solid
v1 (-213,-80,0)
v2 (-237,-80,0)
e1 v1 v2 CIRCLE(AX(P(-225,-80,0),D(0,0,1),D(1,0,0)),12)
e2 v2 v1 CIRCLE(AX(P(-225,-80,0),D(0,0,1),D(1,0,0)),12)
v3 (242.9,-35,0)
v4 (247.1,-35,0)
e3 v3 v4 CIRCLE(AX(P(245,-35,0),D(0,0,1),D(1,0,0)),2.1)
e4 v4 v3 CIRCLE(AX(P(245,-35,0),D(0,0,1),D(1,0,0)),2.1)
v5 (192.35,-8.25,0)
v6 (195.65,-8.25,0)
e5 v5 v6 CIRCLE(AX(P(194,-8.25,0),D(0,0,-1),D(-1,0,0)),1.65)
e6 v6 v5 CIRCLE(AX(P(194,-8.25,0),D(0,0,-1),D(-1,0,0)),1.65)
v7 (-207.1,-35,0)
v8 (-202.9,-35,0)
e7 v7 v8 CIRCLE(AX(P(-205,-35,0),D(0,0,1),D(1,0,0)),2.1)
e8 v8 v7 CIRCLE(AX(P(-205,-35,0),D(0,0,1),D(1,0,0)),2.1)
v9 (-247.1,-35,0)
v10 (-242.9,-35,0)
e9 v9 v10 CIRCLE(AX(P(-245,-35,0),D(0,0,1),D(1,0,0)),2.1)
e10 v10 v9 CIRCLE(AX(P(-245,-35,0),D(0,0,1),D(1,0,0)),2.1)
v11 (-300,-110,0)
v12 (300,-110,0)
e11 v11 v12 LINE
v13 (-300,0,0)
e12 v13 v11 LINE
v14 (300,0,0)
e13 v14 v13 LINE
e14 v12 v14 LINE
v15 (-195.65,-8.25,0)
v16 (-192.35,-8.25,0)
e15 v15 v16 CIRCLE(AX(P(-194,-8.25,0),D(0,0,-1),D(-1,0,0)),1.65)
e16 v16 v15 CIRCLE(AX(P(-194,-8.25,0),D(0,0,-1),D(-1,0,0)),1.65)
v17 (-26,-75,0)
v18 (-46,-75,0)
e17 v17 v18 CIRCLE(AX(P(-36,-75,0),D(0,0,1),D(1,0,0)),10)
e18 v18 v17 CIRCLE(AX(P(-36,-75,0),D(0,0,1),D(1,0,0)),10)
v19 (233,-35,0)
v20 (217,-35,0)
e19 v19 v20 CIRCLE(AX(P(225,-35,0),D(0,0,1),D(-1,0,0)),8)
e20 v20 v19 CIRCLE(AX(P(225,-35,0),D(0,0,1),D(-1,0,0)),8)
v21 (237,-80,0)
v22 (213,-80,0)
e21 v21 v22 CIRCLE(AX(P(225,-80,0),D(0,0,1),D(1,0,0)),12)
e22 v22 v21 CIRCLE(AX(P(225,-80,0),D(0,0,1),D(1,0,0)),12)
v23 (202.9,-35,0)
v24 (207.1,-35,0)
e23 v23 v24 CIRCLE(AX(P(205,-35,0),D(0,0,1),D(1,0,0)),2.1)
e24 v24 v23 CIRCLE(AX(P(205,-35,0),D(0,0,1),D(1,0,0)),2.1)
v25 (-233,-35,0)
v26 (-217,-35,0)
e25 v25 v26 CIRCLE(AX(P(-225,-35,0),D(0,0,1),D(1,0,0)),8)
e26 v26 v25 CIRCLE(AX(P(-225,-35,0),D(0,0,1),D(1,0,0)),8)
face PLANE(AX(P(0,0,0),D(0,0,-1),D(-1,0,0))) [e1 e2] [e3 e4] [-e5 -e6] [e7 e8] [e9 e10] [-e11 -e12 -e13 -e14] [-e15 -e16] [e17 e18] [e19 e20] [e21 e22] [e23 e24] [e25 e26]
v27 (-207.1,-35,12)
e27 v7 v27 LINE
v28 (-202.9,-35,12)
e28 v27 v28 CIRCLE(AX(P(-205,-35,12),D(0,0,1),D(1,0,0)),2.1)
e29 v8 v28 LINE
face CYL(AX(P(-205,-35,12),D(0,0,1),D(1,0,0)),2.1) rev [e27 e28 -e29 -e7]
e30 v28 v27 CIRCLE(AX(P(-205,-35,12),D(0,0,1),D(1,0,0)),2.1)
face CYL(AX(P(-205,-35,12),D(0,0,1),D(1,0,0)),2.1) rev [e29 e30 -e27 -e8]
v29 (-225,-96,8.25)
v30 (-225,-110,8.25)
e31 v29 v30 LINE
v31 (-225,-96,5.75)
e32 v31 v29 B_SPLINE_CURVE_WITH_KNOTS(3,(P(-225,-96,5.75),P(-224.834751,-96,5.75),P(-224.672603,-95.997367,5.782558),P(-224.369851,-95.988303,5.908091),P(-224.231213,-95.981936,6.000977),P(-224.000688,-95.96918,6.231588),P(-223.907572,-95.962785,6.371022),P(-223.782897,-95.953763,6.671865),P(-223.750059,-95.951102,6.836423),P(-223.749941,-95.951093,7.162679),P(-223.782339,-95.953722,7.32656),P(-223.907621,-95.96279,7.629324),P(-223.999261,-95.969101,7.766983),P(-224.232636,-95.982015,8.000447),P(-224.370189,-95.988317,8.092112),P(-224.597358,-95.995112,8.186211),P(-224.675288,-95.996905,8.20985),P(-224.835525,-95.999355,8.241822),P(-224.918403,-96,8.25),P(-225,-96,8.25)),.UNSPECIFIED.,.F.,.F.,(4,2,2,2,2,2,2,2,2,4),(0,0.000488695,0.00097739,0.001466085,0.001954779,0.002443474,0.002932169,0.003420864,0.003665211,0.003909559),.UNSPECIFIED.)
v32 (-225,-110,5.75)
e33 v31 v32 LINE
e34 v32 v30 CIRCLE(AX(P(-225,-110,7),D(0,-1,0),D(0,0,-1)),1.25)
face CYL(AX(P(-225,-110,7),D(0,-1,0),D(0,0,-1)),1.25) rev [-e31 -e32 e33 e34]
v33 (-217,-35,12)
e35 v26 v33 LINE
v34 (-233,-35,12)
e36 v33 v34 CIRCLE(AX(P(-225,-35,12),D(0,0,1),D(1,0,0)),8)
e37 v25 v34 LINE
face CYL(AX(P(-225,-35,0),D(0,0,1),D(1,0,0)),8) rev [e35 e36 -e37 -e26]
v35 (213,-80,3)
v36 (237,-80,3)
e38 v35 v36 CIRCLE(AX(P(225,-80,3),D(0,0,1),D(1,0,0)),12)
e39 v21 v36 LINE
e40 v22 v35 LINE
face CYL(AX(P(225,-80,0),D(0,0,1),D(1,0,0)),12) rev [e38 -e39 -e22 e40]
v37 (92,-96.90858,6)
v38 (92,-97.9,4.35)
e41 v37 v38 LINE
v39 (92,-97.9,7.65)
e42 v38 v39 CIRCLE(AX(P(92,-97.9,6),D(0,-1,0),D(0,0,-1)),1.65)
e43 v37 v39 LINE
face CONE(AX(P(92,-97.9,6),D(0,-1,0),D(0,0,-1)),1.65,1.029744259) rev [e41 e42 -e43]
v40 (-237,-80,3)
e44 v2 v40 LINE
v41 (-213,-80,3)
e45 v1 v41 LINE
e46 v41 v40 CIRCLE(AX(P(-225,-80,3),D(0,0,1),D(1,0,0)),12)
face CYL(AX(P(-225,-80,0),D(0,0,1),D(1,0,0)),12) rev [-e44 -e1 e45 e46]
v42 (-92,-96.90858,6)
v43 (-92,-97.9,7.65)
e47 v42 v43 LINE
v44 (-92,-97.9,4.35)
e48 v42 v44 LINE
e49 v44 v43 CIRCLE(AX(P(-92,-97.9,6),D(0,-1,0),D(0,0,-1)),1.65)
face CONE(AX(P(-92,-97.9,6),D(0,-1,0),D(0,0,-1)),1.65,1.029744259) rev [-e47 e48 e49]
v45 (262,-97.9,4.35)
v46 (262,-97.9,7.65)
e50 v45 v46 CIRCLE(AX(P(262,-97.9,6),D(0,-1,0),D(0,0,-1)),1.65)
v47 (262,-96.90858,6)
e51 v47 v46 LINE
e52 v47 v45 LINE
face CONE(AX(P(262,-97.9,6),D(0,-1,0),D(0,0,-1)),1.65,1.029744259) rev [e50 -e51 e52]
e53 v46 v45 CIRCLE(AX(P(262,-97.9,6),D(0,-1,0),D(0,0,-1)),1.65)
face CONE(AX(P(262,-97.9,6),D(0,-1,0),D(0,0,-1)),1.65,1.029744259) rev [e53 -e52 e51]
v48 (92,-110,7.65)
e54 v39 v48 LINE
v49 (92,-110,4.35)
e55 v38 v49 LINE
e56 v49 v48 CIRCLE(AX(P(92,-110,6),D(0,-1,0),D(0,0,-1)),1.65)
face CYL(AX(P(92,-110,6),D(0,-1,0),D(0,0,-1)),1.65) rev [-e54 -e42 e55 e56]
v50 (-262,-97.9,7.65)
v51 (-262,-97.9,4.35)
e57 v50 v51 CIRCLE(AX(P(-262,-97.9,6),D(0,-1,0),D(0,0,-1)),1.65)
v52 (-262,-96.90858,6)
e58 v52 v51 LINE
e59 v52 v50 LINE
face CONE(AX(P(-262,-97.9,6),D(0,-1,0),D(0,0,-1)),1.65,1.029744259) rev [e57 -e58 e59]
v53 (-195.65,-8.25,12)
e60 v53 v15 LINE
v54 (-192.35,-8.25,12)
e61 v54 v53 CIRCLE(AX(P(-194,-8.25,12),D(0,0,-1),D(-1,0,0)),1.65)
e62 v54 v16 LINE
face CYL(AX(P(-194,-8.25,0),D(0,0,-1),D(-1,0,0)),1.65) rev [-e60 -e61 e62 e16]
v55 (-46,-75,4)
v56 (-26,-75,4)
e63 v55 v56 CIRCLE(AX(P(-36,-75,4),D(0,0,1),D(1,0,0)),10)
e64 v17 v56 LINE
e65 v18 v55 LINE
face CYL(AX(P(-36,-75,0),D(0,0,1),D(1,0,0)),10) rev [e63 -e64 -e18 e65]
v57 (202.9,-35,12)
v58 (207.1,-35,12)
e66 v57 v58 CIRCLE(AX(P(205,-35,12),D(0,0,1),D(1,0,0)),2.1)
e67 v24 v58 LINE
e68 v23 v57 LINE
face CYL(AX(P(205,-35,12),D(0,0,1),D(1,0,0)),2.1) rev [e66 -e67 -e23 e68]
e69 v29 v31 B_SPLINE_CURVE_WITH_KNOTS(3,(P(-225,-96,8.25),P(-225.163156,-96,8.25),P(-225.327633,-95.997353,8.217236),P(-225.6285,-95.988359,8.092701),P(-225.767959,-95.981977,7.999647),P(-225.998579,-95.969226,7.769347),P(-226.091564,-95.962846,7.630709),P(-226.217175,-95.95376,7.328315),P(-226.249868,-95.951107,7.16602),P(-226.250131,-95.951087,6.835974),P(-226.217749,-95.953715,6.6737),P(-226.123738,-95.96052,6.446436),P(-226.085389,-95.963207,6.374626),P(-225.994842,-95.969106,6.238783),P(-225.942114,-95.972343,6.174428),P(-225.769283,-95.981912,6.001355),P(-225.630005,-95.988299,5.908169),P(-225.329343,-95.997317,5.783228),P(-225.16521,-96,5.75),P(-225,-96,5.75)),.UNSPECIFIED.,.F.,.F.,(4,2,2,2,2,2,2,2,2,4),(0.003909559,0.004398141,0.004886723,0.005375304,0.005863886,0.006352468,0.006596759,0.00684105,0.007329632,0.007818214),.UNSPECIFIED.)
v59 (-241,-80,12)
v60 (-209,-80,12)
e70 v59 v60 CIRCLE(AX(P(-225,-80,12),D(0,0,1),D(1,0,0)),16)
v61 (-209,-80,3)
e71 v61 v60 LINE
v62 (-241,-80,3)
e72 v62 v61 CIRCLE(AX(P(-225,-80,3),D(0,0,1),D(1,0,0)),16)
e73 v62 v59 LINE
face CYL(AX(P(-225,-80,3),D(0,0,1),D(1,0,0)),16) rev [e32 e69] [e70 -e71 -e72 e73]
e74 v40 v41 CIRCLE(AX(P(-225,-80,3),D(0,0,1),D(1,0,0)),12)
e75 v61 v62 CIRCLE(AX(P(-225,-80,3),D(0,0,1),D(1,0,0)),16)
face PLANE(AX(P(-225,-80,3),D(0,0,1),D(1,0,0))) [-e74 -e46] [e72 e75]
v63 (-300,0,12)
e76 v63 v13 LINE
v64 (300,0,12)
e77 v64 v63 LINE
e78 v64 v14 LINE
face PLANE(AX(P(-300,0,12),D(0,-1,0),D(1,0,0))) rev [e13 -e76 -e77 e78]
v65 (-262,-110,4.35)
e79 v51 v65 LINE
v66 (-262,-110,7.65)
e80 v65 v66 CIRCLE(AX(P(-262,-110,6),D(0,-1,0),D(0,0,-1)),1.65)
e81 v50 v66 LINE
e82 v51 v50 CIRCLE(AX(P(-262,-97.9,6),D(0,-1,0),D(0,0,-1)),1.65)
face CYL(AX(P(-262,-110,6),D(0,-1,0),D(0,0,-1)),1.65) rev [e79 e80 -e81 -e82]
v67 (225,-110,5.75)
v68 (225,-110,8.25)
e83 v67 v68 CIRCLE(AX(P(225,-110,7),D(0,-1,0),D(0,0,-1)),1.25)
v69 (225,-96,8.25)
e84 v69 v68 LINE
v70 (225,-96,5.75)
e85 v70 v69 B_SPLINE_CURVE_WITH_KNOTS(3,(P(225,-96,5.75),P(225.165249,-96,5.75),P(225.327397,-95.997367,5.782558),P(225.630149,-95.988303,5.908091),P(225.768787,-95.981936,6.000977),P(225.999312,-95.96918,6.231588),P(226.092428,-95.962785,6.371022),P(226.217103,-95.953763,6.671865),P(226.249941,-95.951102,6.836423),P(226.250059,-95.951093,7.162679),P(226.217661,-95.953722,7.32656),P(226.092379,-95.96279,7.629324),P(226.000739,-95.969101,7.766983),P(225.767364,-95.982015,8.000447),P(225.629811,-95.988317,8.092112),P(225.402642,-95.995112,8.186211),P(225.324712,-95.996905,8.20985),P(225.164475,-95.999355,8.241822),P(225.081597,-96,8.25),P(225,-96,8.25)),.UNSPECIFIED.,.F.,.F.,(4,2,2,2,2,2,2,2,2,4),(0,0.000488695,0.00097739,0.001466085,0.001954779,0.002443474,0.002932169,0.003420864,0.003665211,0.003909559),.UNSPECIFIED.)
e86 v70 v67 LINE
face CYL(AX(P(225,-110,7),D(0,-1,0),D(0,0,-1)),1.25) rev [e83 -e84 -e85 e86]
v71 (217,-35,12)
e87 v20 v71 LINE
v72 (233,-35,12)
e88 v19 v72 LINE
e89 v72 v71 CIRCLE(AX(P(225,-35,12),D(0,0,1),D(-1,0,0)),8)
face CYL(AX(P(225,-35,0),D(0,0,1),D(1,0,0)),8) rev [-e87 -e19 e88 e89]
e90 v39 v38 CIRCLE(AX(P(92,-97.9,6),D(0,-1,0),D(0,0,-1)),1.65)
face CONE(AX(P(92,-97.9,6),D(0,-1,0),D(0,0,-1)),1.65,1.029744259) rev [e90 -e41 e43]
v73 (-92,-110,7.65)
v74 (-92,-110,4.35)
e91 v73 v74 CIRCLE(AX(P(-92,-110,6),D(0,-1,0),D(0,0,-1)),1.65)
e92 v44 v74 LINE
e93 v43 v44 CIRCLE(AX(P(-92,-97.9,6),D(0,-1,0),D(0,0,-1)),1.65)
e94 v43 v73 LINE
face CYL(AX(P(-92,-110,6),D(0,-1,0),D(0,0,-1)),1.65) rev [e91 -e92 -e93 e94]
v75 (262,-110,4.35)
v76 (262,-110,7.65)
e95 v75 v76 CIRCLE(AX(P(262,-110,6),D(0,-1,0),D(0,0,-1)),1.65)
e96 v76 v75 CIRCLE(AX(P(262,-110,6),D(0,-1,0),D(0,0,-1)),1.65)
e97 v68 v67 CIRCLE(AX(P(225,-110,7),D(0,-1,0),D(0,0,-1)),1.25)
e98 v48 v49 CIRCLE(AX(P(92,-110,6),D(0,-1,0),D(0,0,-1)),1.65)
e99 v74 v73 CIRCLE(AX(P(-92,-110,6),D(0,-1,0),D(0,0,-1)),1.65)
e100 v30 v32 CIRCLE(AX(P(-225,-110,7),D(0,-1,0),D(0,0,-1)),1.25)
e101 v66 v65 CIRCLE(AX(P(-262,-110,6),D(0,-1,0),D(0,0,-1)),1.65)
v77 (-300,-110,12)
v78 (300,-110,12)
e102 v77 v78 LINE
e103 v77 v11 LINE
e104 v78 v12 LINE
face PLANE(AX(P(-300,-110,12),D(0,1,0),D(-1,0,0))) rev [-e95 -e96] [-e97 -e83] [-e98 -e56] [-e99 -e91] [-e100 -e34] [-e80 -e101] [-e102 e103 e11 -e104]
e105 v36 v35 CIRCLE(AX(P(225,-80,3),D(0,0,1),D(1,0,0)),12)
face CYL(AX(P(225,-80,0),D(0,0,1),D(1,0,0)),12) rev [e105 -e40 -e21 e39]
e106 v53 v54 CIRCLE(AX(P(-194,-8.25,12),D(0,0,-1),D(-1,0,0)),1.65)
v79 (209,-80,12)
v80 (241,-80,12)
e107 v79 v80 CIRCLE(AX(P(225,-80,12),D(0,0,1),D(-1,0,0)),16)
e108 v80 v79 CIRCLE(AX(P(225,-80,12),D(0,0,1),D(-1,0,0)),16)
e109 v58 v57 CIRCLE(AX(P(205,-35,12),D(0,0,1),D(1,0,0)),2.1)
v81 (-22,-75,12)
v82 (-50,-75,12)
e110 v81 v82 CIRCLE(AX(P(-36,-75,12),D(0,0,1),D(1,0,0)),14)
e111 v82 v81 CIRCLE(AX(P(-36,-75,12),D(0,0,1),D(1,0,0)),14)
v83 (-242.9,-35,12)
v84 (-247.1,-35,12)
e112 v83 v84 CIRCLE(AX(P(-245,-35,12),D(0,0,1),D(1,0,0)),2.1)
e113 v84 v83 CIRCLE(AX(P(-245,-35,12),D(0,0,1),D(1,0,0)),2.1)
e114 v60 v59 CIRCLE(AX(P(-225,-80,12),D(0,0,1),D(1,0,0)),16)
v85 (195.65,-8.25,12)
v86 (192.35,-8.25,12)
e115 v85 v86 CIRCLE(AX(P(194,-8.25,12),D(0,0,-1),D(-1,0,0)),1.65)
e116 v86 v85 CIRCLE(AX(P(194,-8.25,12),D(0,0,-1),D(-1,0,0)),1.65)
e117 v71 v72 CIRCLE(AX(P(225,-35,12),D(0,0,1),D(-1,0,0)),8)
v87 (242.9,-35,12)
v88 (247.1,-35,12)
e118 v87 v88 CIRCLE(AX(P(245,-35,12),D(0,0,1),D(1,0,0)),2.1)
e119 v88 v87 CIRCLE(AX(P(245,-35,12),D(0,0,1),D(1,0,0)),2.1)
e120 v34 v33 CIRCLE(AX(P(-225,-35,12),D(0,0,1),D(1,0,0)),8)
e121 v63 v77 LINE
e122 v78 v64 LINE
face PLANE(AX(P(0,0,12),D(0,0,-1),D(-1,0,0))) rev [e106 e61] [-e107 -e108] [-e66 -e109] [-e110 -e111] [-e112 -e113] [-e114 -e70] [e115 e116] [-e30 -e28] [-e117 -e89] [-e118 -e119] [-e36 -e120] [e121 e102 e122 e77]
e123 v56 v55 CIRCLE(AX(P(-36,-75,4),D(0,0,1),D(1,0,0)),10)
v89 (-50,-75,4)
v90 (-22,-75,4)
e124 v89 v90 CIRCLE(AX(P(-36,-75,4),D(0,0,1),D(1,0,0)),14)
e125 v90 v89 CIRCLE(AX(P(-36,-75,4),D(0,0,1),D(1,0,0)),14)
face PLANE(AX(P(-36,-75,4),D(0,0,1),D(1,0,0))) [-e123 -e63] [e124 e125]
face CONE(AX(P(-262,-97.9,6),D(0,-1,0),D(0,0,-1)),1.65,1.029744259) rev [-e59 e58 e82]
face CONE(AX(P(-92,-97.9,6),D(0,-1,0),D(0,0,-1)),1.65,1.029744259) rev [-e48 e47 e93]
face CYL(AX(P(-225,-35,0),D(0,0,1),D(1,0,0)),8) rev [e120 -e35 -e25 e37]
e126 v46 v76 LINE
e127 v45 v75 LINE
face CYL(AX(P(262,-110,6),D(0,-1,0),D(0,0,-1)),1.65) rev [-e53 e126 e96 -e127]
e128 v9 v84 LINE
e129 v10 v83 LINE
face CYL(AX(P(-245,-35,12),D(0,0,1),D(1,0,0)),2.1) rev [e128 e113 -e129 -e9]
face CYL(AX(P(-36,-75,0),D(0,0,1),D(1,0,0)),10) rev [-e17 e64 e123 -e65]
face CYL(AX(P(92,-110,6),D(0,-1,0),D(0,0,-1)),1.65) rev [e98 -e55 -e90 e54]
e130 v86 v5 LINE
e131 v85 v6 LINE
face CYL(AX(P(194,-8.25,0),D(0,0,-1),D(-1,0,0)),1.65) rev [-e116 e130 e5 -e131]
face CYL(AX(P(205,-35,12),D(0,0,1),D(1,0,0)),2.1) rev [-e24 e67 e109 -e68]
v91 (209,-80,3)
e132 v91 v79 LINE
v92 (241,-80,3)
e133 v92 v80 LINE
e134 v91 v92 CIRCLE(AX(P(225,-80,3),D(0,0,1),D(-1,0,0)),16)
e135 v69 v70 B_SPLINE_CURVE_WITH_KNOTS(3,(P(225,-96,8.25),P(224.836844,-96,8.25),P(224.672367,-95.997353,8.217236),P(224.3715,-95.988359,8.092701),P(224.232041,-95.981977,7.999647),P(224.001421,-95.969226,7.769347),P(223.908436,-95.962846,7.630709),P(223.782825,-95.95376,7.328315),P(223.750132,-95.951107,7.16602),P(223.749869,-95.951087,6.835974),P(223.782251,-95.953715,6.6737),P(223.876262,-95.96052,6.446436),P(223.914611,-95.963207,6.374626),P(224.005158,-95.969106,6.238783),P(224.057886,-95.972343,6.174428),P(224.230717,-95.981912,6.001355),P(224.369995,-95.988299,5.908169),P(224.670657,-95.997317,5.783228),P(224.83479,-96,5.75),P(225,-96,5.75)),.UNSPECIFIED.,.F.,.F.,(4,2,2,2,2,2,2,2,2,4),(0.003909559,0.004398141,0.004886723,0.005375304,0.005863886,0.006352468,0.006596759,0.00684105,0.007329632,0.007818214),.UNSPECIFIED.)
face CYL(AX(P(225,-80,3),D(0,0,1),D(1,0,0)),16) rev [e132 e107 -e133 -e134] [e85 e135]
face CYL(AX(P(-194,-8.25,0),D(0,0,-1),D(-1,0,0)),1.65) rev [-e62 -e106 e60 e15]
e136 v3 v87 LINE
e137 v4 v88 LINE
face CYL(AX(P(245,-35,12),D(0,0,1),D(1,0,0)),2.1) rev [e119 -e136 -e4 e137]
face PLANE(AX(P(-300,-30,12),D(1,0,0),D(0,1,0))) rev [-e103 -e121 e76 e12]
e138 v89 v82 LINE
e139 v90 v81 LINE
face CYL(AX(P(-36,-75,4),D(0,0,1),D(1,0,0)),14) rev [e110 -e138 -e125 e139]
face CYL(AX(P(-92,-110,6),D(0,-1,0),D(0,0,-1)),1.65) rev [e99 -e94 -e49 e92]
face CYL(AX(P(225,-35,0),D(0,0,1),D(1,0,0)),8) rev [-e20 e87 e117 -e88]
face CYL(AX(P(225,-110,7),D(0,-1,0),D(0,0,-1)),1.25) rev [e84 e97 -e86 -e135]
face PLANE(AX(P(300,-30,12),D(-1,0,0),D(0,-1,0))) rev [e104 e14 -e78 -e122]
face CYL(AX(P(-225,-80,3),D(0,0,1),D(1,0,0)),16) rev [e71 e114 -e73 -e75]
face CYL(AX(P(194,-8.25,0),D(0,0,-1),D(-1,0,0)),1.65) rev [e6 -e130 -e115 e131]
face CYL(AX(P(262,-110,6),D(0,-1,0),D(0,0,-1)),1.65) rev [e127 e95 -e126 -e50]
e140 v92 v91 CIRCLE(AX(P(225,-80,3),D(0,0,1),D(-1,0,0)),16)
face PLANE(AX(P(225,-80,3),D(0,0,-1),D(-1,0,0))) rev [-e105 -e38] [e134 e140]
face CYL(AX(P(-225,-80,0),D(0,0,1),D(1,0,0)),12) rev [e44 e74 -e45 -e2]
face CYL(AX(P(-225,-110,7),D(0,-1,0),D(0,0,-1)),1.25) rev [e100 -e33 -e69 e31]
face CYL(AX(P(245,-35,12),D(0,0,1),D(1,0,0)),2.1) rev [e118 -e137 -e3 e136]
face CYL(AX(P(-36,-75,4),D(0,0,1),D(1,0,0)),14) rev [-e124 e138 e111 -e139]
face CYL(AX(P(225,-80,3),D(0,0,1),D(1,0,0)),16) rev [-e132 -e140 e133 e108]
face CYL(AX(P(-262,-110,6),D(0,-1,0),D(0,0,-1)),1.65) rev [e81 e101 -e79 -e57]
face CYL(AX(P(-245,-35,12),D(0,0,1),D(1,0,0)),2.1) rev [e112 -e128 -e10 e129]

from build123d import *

# Parameters (mm, degrees)
EXTRUDE_1_DEPTH         = 12
SKETCH_2_R              = 16
CUT_EXTRUDE_2_DEPTH     = 9
SKETCH_3_R              = 14
CUT_EXTRUDE_3_DEPTH     = 8
SKETCH_4_R              = 10
CUT_EXTRUDE_4_DEPTH     = 320.631037291
HOLE_WIZARD_M4_2_D      = 3.3
HOLE_WIZARD_M4_3_D      = 3.3
HOLE_WIZARD_M4_3_DEPTH  = 12.1
HOLE_WIZARD_M4_3_TIP    = 0.991420021
HOLE_WIZARD_M3_1_REACH  = 321.756
HOLE_WIZARD_M3_1_BORE_R = 1.25
SKETCH_17_R             = 12
CUT_EXTRUDE_5_DEPTH     = 320.657629385
SKETCH_18_R             = 8
CUT_EXTRUDE_6_DEPTH     = 320.756157129
HOLE_WIZARD_M5_1_D      = 4.2


with BuildPart() as part:
    # 草图1 → 凸台-拉伸1 (new body)
    with BuildSketch(Plane.XY):
        Polygon((-300, -30), (-300, 0), (300, 0), (300, -30), (300, -110), (-300, -110), align=None)
    extrude(amount=EXTRUDE_1_DEPTH)

    # 草图2 → 切除-拉伸2 (cut)
    with BuildSketch(Plane.XY.offset(12)):
        with Locations(Location((225, -80, 0), (0, 0, 180))):
            Circle(SKETCH_2_R)
        with Locations((-225, -80)):
            Circle(SKETCH_2_R)
    extrude(amount=-CUT_EXTRUDE_2_DEPTH, mode=Mode.SUBTRACT)

    # 草图3 → 切除-拉伸3 (cut)
    with BuildSketch(Plane.XY.offset(12)):
        with Locations((-36, -75)):
            Circle(SKETCH_3_R)
    extrude(amount=-CUT_EXTRUDE_3_DEPTH, mode=Mode.SUBTRACT)

    # 草图4 → 切除-拉伸4 (cut, through all)
    with BuildSketch(Plane.XY.offset(4)):
        with Locations((-36, -75)):
            Circle(SKETCH_4_R)
    extrude(amount=-CUT_EXTRUDE_4_DEPTH, mode=Mode.SUBTRACT)

    # M4 螺纹孔2 (through all)
    with Locations(Plane(origin=(0, 0, 0), x_dir=(-1, 0, 0), z_dir=(0, 0, -1))):
        with Locations((-194, -8.25), (194, -8.25)):
            Hole(HOLE_WIZARD_M4_2_D / 2)

    # M4 螺纹孔3
    with Locations(Plane(origin=(0, -110, 0), x_dir=(-1, 0, 0), z_dir=(0, -1, 0))):
        with Locations((-262, -6), (-92, -6), (92, -6), (262, -6)):
            Hole(HOLE_WIZARD_M4_3_D / 2, depth=HOLE_WIZARD_M4_3_DEPTH)
            with Locations((0, 0, -(HOLE_WIZARD_M4_3_DEPTH + HOLE_WIZARD_M4_3_TIP / 2))):  # 118° drill point
                Cone(0, HOLE_WIZARD_M4_3_D / 2, HOLE_WIZARD_M4_3_TIP, mode=Mode.SUBTRACT)

    # M3 螺纹孔1 bore → M3 螺纹孔1 (cut, up to next)
    with BuildSketch(Plane(origin=(0, -110, 0), x_dir=(-1, 0, 0), z_dir=(0, -1, 0)), mode=Mode.PRIVATE) as hole_wizard_m3_1_sk1:
        with Locations((225, -7)):
            Circle(HOLE_WIZARD_M3_1_BORE_R)
    hole_wizard_m3_1_tool1 = extrude(hole_wizard_m3_1_sk1.sketch, amount=-HOLE_WIZARD_M3_1_REACH, mode=Mode.PRIVATE) & part.part
    # M3 螺纹孔1 bore → M3 螺纹孔1 (cut, up to next)
    with BuildSketch(Plane(origin=(0, -110, 0), x_dir=(-1, 0, 0), z_dir=(0, -1, 0)), mode=Mode.PRIVATE) as hole_wizard_m3_1_sk2:
        with Locations((-225, -7)):
            Circle(HOLE_WIZARD_M3_1_BORE_R)
    hole_wizard_m3_1_tool2 = extrude(hole_wizard_m3_1_sk2.sketch, amount=-HOLE_WIZARD_M3_1_REACH, mode=Mode.PRIVATE) & part.part
    add(hole_wizard_m3_1_tool1.solids().sort_by_distance((-225, -110, 7))[0], mode=Mode.SUBTRACT)
    add(hole_wizard_m3_1_tool2.solids().sort_by_distance((225, -110, 7))[0], mode=Mode.SUBTRACT)

    # 草图17 → 切除-拉伸5 (cut, through all)
    with BuildSketch(Plane.XY.offset(3)):
        with Locations((-225, -80)):
            Circle(SKETCH_17_R)
        with Locations((225, -80)):
            Circle(SKETCH_17_R)
    extrude(amount=-CUT_EXTRUDE_5_DEPTH, mode=Mode.SUBTRACT)

    # 草图18 → 切除-拉伸6 (cut, through all)
    with BuildSketch(Plane.XY.offset(12)):
        with Locations((-225, -35)):
            Circle(SKETCH_18_R)
        with Locations((225, -35)):
            Circle(SKETCH_18_R)
    extrude(amount=-CUT_EXTRUDE_6_DEPTH, mode=Mode.SUBTRACT)

    # M5 螺纹孔1 (through all)
    with Locations(Plane.XY.offset(12)):
        with Locations((245, -35), (205, -35), (-245, -35), (-205, -35)):
            Hole(HOLE_WIZARD_M5_1_D / 2)


solid = part.part
